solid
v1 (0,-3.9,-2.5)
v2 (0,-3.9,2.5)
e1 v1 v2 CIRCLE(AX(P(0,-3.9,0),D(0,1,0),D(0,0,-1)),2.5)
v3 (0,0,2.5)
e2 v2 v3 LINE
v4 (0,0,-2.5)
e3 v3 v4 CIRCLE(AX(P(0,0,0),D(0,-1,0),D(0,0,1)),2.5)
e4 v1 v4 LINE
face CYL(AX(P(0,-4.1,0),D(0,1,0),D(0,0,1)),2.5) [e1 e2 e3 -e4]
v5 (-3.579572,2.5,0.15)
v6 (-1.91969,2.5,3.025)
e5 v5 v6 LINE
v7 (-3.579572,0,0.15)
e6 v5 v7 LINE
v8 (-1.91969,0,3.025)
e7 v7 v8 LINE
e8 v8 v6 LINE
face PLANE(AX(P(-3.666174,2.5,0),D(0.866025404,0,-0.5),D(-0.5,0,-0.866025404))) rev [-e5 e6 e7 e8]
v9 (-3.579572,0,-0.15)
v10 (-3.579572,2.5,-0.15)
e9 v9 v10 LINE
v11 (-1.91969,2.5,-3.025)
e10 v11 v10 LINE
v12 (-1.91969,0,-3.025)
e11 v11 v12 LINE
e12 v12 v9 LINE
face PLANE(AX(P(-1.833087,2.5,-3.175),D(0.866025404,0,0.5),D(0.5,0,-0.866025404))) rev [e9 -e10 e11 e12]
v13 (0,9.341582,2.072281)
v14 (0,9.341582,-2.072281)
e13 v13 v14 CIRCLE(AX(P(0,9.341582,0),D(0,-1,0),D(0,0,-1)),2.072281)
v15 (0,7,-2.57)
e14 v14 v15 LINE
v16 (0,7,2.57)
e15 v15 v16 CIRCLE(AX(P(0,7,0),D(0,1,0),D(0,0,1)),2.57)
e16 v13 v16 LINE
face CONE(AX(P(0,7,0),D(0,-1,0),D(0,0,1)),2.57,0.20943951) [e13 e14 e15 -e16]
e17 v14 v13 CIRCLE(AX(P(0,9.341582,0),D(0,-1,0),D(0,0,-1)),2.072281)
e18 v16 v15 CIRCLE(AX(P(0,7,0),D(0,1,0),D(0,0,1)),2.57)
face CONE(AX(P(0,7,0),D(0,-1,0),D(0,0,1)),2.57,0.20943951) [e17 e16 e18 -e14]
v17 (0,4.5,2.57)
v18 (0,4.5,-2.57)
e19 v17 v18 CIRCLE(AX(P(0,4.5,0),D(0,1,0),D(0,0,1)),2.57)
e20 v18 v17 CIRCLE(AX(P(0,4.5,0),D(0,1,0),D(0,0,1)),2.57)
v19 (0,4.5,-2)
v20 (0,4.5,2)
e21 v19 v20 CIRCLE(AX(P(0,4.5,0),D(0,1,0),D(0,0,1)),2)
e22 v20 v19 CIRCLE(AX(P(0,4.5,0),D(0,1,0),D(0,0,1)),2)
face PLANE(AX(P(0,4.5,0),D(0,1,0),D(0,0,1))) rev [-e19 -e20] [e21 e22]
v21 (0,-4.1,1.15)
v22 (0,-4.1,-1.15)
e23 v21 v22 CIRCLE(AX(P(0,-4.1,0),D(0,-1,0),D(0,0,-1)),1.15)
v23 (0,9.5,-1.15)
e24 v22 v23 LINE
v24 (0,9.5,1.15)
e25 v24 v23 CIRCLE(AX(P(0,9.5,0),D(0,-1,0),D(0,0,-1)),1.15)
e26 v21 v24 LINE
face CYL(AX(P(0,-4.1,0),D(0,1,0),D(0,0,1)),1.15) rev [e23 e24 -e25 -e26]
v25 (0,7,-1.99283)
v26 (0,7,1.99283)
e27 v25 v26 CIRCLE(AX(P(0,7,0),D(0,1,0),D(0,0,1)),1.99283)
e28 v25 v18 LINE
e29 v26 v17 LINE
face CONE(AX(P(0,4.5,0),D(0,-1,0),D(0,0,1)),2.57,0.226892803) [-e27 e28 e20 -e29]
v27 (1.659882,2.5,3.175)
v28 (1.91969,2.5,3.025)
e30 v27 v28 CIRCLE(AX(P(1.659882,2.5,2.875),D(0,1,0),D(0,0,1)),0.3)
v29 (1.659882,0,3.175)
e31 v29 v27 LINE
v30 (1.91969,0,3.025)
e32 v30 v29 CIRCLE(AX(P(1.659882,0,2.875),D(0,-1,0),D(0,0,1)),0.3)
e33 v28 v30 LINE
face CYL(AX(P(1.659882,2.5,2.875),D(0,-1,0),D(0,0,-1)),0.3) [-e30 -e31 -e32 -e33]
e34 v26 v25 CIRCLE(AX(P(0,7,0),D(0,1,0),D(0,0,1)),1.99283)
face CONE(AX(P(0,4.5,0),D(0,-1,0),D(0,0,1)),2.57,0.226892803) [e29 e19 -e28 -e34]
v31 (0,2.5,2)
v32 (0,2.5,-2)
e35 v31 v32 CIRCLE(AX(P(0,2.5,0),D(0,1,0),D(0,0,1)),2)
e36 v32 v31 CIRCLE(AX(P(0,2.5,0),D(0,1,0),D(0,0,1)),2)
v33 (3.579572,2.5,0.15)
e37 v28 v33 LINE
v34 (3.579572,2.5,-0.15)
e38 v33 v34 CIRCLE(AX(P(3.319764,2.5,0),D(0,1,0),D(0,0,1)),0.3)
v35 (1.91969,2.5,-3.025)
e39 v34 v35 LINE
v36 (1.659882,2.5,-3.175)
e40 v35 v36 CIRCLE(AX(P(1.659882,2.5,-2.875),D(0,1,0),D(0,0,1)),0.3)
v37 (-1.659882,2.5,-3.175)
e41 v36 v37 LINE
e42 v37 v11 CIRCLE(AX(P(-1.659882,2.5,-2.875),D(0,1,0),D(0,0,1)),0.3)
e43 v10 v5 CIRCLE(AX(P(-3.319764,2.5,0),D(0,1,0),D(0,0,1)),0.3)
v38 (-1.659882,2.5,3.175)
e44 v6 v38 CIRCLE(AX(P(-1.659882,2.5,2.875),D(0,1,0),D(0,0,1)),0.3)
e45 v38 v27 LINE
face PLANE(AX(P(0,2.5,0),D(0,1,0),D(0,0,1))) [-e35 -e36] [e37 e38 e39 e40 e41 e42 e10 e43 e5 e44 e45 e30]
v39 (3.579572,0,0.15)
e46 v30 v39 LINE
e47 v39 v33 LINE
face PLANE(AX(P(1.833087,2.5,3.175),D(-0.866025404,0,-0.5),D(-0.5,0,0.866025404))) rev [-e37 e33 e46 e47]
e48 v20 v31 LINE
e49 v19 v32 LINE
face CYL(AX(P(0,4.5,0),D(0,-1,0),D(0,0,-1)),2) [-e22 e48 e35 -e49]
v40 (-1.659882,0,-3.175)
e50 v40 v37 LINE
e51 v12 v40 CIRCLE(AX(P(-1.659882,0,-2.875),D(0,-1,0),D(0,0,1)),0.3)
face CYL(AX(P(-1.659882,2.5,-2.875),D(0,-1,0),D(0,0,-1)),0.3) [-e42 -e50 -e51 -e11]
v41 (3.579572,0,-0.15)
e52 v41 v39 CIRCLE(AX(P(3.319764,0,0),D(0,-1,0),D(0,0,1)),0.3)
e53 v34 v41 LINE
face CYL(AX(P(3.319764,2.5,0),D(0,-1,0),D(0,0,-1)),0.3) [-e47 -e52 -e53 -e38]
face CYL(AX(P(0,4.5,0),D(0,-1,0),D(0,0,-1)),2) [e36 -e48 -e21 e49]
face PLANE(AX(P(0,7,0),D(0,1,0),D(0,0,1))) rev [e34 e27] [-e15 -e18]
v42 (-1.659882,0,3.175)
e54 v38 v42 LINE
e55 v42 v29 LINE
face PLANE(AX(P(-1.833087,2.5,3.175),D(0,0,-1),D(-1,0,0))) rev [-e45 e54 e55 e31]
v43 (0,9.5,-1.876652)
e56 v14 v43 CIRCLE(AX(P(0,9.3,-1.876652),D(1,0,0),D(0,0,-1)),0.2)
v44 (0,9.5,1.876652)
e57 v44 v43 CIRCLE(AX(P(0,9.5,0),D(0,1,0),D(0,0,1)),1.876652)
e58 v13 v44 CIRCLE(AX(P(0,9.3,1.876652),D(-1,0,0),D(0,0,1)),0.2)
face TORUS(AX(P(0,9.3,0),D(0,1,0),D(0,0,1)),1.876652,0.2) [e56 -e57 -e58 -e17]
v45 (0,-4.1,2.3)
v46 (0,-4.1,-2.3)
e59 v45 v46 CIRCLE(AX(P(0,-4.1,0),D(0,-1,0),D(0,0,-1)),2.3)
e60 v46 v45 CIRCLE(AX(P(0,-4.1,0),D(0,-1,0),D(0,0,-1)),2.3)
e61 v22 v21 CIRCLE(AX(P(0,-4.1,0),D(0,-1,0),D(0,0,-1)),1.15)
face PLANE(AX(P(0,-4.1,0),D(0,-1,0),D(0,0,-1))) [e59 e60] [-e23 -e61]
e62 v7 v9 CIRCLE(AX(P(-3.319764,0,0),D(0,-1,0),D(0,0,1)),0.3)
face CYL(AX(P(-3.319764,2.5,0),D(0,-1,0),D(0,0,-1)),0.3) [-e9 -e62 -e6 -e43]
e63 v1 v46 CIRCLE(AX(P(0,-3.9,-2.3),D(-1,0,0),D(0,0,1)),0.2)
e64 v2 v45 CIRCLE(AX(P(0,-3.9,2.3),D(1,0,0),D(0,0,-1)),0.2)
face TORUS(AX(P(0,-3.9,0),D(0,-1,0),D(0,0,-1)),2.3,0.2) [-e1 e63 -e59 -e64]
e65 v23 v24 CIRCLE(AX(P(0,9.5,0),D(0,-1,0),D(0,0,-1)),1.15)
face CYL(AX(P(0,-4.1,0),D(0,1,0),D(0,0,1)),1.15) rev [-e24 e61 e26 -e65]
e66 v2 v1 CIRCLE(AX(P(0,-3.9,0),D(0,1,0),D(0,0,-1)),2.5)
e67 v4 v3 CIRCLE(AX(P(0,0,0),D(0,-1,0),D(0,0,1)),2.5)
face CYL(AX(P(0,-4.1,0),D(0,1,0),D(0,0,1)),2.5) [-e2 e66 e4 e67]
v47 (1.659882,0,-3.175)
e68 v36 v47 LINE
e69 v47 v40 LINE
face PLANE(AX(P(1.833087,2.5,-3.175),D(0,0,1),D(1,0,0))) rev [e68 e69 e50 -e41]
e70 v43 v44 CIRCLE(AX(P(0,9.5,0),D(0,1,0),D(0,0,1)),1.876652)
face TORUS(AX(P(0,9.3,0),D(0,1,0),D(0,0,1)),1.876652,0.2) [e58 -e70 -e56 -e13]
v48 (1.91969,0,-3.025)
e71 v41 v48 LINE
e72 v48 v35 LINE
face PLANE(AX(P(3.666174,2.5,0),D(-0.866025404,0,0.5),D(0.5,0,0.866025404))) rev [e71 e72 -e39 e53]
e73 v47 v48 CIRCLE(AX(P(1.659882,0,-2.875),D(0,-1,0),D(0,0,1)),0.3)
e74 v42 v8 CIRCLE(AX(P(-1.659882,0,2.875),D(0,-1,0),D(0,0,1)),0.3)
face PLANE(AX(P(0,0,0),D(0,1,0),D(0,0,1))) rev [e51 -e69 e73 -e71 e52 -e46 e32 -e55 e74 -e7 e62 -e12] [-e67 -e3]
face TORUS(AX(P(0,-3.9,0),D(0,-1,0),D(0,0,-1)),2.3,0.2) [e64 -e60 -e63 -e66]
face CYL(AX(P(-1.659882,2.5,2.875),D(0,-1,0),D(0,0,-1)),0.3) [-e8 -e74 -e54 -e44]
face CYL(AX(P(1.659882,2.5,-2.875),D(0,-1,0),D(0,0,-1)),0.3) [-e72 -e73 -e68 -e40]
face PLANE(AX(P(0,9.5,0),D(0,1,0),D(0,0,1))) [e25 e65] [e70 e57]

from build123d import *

# Parameters (mm, degrees)
BOSS_EXTRUDE1_DEPTH = 2.5
SKETCH2_R           = 2
BOSS_EXTRUDE2_DEPTH = 2
SKETCH3_R           = 2.57
BOSS_EXTRUDE3_DEPTH = 2.5
BOSS_EXTRUDE3_TAPER = 13
SKETCH4_R           = 2.57
BOSS_EXTRUDE4_DEPTH = 2.5
BOSS_EXTRUDE4_TAPER = 12
SKETCH5_R           = 2.5
SKETCH5_R_2         = 1.15
BOSS_EXTRUDE5_DEPTH = 4.1
SKETCH6_R           = 1.15
CUT_EXTRUDE1_DEPTH  = 11.666370528
FILLET1_R           = 0.3
FILLET2_R           = 0.2


with BuildPart() as part:
    # Sketch1 → Boss-Extrude1 (new body)
    with BuildSketch(Plane(origin=(0, 0, 0), x_dir=(1, 0, 0), z_dir=(0, 1, 0))):
        Polygon((3.666174209, 0), (1.833087105, 3.175), (-1.833087105, 3.175), (-3.666174209, 0), (-1.833087105, -3.175), (1.833087105, -3.175), align=None)
    extrude(amount=BOSS_EXTRUDE1_DEPTH)

    # Sketch2 → Boss-Extrude2 (add)
    with BuildSketch(Plane(origin=(0, 2.5, 0), x_dir=(1, 0, 0), z_dir=(0, 1, 0))):
        with Locations(Location((0, 0, 0), (0, 0, 270))):
            Circle(SKETCH2_R)
    extrude(amount=BOSS_EXTRUDE2_DEPTH)

    # Sketch3 → Boss-Extrude3 (add)
    with BuildSketch(Plane(origin=(0, 4.5, 0), x_dir=(1, 0, 0), z_dir=(0, 1, 0))):
        Circle(SKETCH3_R)
    extrude(amount=BOSS_EXTRUDE3_DEPTH, taper=BOSS_EXTRUDE3_TAPER)

    # Sketch4 → Boss-Extrude4 (add)
    with BuildSketch(Plane(origin=(0, 7, 0), x_dir=(1, 0, 0), z_dir=(0, 1, 0))):
        Circle(SKETCH4_R)
    extrude(amount=BOSS_EXTRUDE4_DEPTH, taper=BOSS_EXTRUDE4_TAPER)

    # Sketch5 → Boss-Extrude5 (add)
    with BuildSketch(Plane.XZ):
        with Locations(Location((0, 0, 0), (0, 0, 90))):
            Circle(SKETCH5_R)
        with Locations(Location((0, 0, 0), (0, 0, 270))):
            Circle(SKETCH5_R_2, mode=Mode.SUBTRACT)
    extrude(amount=BOSS_EXTRUDE5_DEPTH)

    # Sketch6 → Cut-Extrude1 (cut, through all)
    with BuildSketch(Plane.XZ):
        with Locations(Location((0, 0, 0), (0, 0, 270))):
            Circle(SKETCH6_R)
    extrude(amount=-CUT_EXTRUDE1_DEPTH, mode=Mode.SUBTRACT)

    # Fillet1
    fillet1_edges = [part.edges().sort_by_distance(p)[0] for p in [
        (1.833087105, 1.25, 3.175),
        (-1.833087105, 1.25, 3.175),
        (-3.666174209, 1.25, 0),
        (-1.833087105, 1.25, -3.175),
        (1.833087105, 1.25, -3.175),
        (3.666174209, 1.25, 0),
    ]]
    fillet(fillet1_edges, radius=FILLET1_R)

    # Fillet2
    fillet2_edges = [part.edges().sort_by_distance(p)[0] for p in [
        (-2.038608596, 9.5, 0),
        (0, -4.1, -2.5),
    ]]
    fillet(fillet2_edges, radius=FILLET2_R)


solid = part.part
